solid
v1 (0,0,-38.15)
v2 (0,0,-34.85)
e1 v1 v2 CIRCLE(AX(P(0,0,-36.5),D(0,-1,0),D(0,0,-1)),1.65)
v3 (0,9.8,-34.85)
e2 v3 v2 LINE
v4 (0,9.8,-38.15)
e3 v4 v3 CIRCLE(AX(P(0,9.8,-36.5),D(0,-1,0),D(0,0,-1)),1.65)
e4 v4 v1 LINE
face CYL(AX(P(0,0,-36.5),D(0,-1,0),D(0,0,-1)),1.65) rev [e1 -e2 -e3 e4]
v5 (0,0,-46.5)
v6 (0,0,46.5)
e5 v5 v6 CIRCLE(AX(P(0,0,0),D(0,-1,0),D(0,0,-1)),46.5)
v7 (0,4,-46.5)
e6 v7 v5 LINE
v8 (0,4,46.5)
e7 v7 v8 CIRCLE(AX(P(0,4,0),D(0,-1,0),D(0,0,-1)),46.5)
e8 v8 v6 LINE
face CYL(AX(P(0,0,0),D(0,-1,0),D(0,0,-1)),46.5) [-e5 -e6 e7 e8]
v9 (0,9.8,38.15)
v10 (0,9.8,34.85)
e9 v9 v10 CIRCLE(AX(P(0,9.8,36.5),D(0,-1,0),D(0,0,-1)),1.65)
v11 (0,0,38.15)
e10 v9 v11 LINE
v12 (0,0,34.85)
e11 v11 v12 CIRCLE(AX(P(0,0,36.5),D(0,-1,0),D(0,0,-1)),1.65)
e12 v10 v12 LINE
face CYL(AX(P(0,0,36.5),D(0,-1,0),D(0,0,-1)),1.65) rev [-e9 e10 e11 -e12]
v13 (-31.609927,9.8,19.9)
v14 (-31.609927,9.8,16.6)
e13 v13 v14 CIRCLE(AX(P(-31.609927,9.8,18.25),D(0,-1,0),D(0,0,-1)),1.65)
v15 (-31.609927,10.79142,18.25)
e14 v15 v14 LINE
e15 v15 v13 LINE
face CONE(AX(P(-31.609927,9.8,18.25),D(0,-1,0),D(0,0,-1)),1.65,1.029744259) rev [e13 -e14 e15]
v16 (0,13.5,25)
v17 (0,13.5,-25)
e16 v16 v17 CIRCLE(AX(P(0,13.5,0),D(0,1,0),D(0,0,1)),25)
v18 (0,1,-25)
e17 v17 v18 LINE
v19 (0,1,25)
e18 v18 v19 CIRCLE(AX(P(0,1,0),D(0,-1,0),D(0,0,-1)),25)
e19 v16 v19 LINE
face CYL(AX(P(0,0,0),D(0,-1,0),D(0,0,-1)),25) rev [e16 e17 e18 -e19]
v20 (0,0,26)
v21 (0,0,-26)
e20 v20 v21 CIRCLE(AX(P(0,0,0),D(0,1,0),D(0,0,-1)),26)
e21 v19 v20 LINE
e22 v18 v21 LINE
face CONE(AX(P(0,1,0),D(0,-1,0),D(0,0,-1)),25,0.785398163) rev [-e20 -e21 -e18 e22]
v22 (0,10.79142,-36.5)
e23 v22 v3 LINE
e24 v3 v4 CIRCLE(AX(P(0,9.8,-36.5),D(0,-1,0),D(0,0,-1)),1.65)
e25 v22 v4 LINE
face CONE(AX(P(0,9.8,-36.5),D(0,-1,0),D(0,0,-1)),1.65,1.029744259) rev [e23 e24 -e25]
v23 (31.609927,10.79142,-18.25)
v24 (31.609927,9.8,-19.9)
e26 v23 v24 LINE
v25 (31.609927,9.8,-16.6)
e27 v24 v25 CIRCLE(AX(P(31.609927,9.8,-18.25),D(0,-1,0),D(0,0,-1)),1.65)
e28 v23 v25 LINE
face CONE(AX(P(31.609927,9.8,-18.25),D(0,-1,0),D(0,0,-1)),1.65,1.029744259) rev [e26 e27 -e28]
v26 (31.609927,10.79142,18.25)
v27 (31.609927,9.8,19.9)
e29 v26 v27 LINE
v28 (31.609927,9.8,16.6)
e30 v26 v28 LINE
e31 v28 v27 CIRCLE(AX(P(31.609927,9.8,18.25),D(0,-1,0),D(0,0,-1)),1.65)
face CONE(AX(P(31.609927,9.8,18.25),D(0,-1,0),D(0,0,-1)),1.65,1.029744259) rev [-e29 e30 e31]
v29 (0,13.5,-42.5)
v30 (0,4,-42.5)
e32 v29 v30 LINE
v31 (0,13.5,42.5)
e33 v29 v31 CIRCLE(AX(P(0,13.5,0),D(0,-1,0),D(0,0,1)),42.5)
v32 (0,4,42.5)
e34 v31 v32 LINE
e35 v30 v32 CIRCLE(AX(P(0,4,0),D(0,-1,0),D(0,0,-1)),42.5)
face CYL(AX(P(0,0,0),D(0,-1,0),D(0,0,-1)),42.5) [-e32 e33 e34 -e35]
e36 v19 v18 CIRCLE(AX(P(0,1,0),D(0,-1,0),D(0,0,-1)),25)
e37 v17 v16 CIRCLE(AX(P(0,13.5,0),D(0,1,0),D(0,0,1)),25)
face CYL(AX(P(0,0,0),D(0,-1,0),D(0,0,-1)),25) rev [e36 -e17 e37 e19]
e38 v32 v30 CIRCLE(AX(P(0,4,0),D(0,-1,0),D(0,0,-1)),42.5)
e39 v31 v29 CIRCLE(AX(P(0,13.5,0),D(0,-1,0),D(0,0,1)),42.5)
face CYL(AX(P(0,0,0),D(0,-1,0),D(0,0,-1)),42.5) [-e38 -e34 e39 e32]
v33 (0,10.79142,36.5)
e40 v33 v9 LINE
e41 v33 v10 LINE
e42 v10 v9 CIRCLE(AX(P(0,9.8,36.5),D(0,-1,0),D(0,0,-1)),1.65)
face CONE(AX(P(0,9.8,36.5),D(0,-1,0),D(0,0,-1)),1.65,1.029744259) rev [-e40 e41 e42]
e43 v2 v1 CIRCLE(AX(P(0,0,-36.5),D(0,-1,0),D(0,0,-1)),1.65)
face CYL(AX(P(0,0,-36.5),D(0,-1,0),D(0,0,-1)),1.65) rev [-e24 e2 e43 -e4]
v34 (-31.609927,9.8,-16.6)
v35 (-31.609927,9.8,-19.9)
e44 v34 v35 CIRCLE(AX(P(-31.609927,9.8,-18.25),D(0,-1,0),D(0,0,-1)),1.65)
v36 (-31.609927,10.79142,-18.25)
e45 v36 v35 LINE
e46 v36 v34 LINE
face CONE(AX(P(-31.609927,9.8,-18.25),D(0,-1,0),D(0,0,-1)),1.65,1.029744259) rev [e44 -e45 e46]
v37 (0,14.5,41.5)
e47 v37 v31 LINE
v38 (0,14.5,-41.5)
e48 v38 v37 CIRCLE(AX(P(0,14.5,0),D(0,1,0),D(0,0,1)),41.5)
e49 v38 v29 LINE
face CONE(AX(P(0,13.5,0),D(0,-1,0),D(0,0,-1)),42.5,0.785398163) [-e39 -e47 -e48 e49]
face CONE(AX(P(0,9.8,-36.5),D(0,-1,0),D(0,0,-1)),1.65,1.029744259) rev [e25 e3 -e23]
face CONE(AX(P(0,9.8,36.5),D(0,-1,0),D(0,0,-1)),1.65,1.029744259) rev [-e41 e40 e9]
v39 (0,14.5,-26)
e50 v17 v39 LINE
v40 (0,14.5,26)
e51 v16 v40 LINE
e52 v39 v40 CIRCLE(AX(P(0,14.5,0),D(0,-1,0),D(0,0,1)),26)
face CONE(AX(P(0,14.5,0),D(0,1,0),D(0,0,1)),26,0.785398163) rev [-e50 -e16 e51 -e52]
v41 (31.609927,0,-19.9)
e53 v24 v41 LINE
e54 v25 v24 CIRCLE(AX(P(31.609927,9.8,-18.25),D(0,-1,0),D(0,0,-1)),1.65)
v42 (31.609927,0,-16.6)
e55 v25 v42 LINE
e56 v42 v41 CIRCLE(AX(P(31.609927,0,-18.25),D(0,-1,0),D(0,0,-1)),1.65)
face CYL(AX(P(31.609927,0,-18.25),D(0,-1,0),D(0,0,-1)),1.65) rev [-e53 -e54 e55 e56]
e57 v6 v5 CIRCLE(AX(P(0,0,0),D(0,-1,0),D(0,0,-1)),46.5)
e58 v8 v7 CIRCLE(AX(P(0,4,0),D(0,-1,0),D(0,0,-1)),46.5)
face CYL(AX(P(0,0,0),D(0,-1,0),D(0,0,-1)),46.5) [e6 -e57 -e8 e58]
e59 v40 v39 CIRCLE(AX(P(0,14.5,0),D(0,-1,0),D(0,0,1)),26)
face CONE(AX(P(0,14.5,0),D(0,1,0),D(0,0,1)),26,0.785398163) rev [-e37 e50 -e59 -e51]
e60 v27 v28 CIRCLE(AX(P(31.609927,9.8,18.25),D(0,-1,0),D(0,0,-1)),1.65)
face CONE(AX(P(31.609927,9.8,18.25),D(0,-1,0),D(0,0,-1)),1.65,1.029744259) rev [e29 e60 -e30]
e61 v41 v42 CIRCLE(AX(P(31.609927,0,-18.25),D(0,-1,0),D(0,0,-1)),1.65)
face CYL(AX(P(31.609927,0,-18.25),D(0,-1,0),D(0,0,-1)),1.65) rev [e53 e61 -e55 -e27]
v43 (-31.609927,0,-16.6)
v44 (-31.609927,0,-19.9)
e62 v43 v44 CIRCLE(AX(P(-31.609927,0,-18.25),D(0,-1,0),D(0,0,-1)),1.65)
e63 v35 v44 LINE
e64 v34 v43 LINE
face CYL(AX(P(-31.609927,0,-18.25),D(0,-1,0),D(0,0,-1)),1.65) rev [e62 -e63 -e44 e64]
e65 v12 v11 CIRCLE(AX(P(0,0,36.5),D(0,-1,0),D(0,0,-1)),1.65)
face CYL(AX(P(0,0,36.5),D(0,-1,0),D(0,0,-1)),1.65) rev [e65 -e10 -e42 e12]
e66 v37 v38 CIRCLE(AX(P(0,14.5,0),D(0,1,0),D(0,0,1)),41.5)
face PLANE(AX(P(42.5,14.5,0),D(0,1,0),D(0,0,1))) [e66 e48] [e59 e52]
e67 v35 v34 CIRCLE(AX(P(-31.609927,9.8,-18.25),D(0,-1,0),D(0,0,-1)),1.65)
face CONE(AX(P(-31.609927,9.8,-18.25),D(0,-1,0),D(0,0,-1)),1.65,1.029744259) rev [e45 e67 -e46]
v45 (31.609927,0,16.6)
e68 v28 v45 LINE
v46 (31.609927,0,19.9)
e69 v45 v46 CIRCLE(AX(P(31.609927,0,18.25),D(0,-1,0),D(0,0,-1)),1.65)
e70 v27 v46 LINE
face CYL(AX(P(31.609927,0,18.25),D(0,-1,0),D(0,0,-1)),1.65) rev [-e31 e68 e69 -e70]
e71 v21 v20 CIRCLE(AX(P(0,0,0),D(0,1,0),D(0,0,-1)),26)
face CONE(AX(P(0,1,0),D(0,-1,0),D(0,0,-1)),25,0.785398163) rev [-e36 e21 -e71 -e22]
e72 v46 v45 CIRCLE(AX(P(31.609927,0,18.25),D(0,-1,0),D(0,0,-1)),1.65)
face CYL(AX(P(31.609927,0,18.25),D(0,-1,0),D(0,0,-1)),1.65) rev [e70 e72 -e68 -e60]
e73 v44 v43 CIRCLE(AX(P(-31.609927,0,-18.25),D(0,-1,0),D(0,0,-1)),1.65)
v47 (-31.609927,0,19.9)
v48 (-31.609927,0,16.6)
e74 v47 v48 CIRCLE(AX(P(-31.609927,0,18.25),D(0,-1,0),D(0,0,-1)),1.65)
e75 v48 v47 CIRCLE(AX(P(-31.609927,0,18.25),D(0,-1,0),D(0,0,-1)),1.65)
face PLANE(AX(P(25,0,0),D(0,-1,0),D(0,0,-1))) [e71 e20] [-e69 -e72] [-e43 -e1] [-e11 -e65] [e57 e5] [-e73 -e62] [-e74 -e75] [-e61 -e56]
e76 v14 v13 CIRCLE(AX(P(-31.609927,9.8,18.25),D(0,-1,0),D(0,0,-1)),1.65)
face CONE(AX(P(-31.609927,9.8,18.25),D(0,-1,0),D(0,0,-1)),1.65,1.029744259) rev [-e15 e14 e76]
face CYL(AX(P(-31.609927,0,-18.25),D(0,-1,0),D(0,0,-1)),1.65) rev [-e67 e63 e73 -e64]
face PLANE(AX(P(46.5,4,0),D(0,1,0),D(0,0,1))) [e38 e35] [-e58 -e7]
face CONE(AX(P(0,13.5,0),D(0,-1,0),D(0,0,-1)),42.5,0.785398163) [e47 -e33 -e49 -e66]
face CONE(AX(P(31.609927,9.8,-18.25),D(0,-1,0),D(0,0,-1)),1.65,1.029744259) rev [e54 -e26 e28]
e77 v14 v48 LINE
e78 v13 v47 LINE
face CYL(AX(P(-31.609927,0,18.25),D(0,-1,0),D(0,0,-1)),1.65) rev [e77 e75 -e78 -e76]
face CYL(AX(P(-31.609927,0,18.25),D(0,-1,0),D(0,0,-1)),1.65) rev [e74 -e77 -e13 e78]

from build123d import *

# Parameters (mm, degrees)
M4_TAPPED_HOLE1_D     = 3.3
M4_TAPPED_HOLE1_DEPTH = 9.8
M4_TAPPED_HOLE1_TIP   = 0.991420021
CHAMFER1_SIZE         = 1


with BuildPart() as part:
    # Sketch1 → Revolve1 (revolve)
    with BuildSketch(Plane.XY, mode=Mode.PRIVATE) as revolve1_sk:
        Polygon((25, 0), (46.5, 0), (46.5, 4), (42.5, 4), (42.5, 14.5), (25, 14.5), align=None)
    revolve(revolve1_sk.sketch.rotate(Axis((0, 0, 0), (0, 1, 0)), 90), axis=Axis((0, 0, 0), (0, 1, 0)))

    # M4 Tapped Hole1
    with Locations(Plane(origin=(0, 0, 0), x_dir=(-1, 0, 0), z_dir=(0, -1, 0))):
        with Locations((0, -36.5), (-31.609927238, -18.25), (-31.609927238, 18.25), (0, 36.5), (31.609927238, 18.25), (31.609927238, -18.25)):
            Hole(M4_TAPPED_HOLE1_D / 2, depth=M4_TAPPED_HOLE1_DEPTH)
            with Locations((0, 0, -(M4_TAPPED_HOLE1_DEPTH + M4_TAPPED_HOLE1_TIP / 2))):  # 118° drill point
                Cone(0, M4_TAPPED_HOLE1_D / 2, M4_TAPPED_HOLE1_TIP, mode=Mode.SUBTRACT)

    # Chamfer1
    chamfer1_edges = [part.edges().sort_by_distance(p)[0] for p in [
        (0, 0, 25),
        (0, 14.5, 25),
        (0, 14.5, 42.5),
    ]]
    chamfer(chamfer1_edges, length=CHAMFER1_SIZE)


solid = part.part
